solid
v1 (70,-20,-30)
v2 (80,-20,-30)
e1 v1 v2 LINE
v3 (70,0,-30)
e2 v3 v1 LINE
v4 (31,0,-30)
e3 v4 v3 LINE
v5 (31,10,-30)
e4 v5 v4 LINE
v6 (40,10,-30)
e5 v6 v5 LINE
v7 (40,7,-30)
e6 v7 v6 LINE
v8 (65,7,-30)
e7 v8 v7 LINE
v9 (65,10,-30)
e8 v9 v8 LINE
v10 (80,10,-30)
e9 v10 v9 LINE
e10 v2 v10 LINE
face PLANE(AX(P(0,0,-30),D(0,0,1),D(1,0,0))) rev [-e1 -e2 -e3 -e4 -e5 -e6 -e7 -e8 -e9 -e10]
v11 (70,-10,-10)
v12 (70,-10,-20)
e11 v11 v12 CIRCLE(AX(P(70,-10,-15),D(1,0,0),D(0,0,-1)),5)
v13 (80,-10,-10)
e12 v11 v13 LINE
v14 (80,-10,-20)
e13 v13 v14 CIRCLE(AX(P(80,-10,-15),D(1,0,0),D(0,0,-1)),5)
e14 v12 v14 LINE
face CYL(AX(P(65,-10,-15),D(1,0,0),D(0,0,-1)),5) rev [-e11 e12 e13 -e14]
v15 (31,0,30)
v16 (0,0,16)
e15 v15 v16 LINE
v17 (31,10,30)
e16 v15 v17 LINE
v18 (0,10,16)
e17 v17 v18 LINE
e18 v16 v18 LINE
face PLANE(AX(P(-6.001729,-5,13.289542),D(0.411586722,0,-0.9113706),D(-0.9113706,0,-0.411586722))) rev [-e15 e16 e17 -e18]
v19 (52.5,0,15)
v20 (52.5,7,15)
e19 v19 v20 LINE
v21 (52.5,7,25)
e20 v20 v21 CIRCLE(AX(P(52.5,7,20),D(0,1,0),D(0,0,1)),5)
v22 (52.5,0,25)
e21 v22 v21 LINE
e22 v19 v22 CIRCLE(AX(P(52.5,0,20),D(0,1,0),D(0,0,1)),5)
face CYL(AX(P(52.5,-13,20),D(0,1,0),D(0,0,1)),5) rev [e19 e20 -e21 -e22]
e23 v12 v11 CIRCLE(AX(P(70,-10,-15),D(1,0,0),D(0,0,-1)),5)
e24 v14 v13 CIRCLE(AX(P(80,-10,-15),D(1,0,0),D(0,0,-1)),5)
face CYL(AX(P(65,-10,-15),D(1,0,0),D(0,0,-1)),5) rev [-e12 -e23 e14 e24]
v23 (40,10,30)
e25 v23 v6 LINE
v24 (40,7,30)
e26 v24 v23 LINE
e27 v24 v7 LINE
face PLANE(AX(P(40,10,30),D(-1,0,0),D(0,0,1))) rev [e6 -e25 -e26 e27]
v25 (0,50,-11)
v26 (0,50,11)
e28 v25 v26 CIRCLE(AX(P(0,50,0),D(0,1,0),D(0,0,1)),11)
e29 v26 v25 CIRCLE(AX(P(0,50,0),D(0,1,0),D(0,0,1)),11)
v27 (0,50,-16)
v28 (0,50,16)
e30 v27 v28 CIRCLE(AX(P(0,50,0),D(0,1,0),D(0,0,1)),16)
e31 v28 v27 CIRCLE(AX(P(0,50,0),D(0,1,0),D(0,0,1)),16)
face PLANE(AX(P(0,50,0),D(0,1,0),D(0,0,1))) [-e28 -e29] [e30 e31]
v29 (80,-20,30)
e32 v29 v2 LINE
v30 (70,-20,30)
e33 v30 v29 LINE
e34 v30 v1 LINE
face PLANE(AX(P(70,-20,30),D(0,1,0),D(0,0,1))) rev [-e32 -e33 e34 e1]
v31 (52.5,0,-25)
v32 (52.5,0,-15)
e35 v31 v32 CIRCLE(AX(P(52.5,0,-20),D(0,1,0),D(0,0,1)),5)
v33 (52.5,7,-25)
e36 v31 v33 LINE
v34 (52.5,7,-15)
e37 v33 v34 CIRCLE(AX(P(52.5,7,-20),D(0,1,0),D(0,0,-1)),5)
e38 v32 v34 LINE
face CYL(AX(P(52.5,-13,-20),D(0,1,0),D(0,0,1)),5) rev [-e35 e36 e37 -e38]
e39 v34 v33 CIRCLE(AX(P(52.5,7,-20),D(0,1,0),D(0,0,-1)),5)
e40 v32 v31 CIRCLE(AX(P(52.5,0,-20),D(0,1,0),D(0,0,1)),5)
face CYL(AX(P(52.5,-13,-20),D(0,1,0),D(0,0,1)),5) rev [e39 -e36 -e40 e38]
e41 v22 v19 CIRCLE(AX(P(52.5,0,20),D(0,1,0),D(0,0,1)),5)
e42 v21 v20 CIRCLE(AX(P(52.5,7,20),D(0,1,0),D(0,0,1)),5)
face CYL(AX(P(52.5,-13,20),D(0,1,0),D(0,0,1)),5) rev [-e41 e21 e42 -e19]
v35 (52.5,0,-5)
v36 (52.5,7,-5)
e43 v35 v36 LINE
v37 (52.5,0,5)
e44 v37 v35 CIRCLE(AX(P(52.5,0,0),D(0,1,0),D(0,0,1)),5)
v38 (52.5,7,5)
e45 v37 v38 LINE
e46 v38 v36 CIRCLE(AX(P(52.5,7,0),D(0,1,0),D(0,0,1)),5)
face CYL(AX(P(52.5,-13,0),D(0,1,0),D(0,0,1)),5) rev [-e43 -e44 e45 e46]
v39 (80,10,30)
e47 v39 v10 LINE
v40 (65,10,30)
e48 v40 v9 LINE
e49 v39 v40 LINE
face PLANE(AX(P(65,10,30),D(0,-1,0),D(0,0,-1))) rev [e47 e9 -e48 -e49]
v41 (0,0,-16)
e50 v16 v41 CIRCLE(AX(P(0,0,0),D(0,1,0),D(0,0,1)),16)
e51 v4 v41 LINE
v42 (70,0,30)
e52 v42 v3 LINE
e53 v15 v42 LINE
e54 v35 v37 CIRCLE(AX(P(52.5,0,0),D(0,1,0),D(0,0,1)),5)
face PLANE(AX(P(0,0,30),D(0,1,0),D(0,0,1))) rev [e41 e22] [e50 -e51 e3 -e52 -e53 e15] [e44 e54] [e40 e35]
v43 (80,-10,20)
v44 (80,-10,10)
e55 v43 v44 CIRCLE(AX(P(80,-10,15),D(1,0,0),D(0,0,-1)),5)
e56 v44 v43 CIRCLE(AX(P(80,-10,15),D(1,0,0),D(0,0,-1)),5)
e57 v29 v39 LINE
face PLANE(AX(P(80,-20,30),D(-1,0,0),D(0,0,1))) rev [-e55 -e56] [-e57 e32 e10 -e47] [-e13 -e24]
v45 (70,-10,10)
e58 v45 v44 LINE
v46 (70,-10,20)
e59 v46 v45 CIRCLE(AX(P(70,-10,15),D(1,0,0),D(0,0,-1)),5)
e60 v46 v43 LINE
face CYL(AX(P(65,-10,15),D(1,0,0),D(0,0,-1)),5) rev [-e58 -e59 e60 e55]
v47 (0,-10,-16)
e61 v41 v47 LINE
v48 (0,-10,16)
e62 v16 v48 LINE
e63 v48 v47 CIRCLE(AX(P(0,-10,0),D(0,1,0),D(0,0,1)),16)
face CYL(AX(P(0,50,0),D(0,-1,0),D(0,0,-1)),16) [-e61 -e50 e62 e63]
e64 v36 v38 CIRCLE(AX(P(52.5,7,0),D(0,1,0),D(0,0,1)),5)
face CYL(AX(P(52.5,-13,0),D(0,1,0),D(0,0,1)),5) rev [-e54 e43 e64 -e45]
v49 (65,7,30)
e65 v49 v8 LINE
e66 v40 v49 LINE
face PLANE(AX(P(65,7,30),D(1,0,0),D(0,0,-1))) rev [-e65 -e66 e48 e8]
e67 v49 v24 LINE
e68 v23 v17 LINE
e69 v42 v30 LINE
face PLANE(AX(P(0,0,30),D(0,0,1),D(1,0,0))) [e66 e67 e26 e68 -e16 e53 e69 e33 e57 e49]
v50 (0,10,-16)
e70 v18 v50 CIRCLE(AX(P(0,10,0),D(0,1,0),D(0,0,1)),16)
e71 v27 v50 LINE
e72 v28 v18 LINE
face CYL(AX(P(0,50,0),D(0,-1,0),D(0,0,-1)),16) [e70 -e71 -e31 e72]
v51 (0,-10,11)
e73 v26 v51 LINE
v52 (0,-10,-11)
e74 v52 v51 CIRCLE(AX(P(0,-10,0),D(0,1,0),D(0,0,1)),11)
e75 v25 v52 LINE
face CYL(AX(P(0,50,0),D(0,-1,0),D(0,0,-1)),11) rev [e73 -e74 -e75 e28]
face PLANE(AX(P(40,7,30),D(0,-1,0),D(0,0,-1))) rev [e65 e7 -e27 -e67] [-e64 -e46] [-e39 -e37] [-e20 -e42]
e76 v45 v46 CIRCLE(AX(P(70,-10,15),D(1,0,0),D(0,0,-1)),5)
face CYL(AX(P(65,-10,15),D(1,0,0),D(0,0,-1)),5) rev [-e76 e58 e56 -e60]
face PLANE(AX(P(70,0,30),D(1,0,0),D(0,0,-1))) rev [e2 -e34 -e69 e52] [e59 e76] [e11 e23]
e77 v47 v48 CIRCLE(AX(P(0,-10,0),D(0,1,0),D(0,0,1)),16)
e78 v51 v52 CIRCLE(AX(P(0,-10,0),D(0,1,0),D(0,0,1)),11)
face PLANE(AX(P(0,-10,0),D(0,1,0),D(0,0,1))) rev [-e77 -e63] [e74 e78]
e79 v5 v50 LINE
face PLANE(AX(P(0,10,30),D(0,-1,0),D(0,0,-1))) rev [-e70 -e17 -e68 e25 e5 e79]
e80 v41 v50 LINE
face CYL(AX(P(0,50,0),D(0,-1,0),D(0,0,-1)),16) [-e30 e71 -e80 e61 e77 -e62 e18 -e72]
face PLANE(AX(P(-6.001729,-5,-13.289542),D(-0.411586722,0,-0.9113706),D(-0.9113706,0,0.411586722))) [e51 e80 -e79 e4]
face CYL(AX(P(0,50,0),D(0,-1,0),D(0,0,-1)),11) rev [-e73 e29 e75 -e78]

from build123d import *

# Parameters (mm, degrees)
BRACKET_BODY_60MM_DEPTH      = 30
TOP_HOLES_SKETCH_R           = 5
TOP_HOLES_DEPTH              = 15
TOP_GROOVE_CUT_DEPTH         = 15
HINGE_TUBE_UPPER_SKETCH_R    = 16
HINGE_TUBE_UPPER_SKETCH_R_2  = 11
HINGE_TUBE_UPPER_32X40_DEPTH = 40
HINGE_START                  = -20
HINGE_TUBE_LOWER_SKETCH_R    = 16
HINGE_TUBE_LOWER_SKETCH_R_2  = 11
HINGE_TUBE_LOWER_32X20_DEPTH = 20
HINGE_BORE_SKETCH_R          = 11
HINGE_BORE_22_DEPTH          = 20
SIDE_HOLES_SKETCH_R          = 5
SIDE_HOLES_DEPTH             = 20


with BuildPart() as part:
    # Bracket Profile Sketch → Bracket Body 60mm (new, symmetric)
    with BuildSketch(Plane.XY):
        Polygon((0, 0), (70, 0), (70, -20), (80, -20), (80, 10), (65, 10), (65, 7), (40, 7), (40, 10), (0, 10), align=None)
    extrude(amount=BRACKET_BODY_60MM_DEPTH, both=True)

    # Top Holes Sketch → Top Holes (cut)
    with BuildSketch(Plane(origin=(80, 0, 0), x_dir=(0, 0, -1), z_dir=(1, 0, 0))):
        with Locations((-15, -10)):
            Circle(TOP_HOLES_SKETCH_R)
        with Locations((15, -10)):
            Circle(TOP_HOLES_SKETCH_R)
    extrude(amount=-TOP_HOLES_DEPTH, mode=Mode.SUBTRACT)

    # Top Groove Sketch → Top Groove Cut (cut)
    with BuildSketch(Plane(origin=(0, 10, 0), x_dir=(1, 0, 0), z_dir=(0, 1, 0))):
        Polygon((0, 16), (31, 30), (0, 30), align=None)
        Polygon((31, -30), (0, -16), (0, -30), align=None)
    extrude(amount=-TOP_GROOVE_CUT_DEPTH, mode=Mode.SUBTRACT)

    # Hinge Tube Upper Sketch → Hinge Tube Upper Ø32x40 (add)
    with BuildSketch(Plane(origin=(0, 10, 0), x_dir=(1, 0, 0), z_dir=(0, 1, 0))):
        with Locations(Location((0, 0, 0), (0, 0, 270))):
            Circle(HINGE_TUBE_UPPER_SKETCH_R)
        with Locations(Location((0, 0, 0), (0, 0, 270))):
            Circle(HINGE_TUBE_UPPER_SKETCH_R_2, mode=Mode.SUBTRACT)
    extrude(amount=HINGE_TUBE_UPPER_32X40_DEPTH)

    # Hinge Tube Lower Sketch → Hinge Tube Lower Ø32x20 (add)
    with BuildSketch(Plane(origin=(0, 10, 0), x_dir=(1, 0, 0), z_dir=(0, 1, 0)).offset(HINGE_START)):
        with Locations(Location((0, 0, 0), (0, 0, 270))):
            Circle(HINGE_TUBE_LOWER_SKETCH_R)
        with Locations(Location((0, 0, 0), (0, 0, 270))):
            Circle(HINGE_TUBE_LOWER_SKETCH_R_2, mode=Mode.SUBTRACT)
    extrude(amount=HINGE_TUBE_LOWER_32X20_DEPTH)

    # Hinge Bore Sketch → Hinge Bore Ø22 (cut)
    with BuildSketch(Plane(origin=(0, 10, 0), x_dir=(1, 0, 0), z_dir=(0, 1, 0)).offset(HINGE_START)):
        with Locations(Location((0, 0, 0), (0, 0, 270))):
            Circle(HINGE_BORE_SKETCH_R)
    extrude(amount=HINGE_BORE_22_DEPTH, mode=Mode.SUBTRACT)

    # Side Holes Sketch → Side Holes (cut)
    with BuildSketch(Plane(origin=(0, 7, 0), x_dir=(1, 0, 0), z_dir=(0, 1, 0))):
        with Locations(Location((52.5, -20, 0), (0, 0, 270))):
            Circle(SIDE_HOLES_SKETCH_R)
        with Locations(Location((52.5, 0, 0), (0, 0, 270))):
            Circle(SIDE_HOLES_SKETCH_R)
        with Locations(Location((52.5, 20, 0), (0, 0, 270))):
            Circle(SIDE_HOLES_SKETCH_R)
    extrude(amount=-SIDE_HOLES_DEPTH, mode=Mode.SUBTRACT)


solid = part.part
